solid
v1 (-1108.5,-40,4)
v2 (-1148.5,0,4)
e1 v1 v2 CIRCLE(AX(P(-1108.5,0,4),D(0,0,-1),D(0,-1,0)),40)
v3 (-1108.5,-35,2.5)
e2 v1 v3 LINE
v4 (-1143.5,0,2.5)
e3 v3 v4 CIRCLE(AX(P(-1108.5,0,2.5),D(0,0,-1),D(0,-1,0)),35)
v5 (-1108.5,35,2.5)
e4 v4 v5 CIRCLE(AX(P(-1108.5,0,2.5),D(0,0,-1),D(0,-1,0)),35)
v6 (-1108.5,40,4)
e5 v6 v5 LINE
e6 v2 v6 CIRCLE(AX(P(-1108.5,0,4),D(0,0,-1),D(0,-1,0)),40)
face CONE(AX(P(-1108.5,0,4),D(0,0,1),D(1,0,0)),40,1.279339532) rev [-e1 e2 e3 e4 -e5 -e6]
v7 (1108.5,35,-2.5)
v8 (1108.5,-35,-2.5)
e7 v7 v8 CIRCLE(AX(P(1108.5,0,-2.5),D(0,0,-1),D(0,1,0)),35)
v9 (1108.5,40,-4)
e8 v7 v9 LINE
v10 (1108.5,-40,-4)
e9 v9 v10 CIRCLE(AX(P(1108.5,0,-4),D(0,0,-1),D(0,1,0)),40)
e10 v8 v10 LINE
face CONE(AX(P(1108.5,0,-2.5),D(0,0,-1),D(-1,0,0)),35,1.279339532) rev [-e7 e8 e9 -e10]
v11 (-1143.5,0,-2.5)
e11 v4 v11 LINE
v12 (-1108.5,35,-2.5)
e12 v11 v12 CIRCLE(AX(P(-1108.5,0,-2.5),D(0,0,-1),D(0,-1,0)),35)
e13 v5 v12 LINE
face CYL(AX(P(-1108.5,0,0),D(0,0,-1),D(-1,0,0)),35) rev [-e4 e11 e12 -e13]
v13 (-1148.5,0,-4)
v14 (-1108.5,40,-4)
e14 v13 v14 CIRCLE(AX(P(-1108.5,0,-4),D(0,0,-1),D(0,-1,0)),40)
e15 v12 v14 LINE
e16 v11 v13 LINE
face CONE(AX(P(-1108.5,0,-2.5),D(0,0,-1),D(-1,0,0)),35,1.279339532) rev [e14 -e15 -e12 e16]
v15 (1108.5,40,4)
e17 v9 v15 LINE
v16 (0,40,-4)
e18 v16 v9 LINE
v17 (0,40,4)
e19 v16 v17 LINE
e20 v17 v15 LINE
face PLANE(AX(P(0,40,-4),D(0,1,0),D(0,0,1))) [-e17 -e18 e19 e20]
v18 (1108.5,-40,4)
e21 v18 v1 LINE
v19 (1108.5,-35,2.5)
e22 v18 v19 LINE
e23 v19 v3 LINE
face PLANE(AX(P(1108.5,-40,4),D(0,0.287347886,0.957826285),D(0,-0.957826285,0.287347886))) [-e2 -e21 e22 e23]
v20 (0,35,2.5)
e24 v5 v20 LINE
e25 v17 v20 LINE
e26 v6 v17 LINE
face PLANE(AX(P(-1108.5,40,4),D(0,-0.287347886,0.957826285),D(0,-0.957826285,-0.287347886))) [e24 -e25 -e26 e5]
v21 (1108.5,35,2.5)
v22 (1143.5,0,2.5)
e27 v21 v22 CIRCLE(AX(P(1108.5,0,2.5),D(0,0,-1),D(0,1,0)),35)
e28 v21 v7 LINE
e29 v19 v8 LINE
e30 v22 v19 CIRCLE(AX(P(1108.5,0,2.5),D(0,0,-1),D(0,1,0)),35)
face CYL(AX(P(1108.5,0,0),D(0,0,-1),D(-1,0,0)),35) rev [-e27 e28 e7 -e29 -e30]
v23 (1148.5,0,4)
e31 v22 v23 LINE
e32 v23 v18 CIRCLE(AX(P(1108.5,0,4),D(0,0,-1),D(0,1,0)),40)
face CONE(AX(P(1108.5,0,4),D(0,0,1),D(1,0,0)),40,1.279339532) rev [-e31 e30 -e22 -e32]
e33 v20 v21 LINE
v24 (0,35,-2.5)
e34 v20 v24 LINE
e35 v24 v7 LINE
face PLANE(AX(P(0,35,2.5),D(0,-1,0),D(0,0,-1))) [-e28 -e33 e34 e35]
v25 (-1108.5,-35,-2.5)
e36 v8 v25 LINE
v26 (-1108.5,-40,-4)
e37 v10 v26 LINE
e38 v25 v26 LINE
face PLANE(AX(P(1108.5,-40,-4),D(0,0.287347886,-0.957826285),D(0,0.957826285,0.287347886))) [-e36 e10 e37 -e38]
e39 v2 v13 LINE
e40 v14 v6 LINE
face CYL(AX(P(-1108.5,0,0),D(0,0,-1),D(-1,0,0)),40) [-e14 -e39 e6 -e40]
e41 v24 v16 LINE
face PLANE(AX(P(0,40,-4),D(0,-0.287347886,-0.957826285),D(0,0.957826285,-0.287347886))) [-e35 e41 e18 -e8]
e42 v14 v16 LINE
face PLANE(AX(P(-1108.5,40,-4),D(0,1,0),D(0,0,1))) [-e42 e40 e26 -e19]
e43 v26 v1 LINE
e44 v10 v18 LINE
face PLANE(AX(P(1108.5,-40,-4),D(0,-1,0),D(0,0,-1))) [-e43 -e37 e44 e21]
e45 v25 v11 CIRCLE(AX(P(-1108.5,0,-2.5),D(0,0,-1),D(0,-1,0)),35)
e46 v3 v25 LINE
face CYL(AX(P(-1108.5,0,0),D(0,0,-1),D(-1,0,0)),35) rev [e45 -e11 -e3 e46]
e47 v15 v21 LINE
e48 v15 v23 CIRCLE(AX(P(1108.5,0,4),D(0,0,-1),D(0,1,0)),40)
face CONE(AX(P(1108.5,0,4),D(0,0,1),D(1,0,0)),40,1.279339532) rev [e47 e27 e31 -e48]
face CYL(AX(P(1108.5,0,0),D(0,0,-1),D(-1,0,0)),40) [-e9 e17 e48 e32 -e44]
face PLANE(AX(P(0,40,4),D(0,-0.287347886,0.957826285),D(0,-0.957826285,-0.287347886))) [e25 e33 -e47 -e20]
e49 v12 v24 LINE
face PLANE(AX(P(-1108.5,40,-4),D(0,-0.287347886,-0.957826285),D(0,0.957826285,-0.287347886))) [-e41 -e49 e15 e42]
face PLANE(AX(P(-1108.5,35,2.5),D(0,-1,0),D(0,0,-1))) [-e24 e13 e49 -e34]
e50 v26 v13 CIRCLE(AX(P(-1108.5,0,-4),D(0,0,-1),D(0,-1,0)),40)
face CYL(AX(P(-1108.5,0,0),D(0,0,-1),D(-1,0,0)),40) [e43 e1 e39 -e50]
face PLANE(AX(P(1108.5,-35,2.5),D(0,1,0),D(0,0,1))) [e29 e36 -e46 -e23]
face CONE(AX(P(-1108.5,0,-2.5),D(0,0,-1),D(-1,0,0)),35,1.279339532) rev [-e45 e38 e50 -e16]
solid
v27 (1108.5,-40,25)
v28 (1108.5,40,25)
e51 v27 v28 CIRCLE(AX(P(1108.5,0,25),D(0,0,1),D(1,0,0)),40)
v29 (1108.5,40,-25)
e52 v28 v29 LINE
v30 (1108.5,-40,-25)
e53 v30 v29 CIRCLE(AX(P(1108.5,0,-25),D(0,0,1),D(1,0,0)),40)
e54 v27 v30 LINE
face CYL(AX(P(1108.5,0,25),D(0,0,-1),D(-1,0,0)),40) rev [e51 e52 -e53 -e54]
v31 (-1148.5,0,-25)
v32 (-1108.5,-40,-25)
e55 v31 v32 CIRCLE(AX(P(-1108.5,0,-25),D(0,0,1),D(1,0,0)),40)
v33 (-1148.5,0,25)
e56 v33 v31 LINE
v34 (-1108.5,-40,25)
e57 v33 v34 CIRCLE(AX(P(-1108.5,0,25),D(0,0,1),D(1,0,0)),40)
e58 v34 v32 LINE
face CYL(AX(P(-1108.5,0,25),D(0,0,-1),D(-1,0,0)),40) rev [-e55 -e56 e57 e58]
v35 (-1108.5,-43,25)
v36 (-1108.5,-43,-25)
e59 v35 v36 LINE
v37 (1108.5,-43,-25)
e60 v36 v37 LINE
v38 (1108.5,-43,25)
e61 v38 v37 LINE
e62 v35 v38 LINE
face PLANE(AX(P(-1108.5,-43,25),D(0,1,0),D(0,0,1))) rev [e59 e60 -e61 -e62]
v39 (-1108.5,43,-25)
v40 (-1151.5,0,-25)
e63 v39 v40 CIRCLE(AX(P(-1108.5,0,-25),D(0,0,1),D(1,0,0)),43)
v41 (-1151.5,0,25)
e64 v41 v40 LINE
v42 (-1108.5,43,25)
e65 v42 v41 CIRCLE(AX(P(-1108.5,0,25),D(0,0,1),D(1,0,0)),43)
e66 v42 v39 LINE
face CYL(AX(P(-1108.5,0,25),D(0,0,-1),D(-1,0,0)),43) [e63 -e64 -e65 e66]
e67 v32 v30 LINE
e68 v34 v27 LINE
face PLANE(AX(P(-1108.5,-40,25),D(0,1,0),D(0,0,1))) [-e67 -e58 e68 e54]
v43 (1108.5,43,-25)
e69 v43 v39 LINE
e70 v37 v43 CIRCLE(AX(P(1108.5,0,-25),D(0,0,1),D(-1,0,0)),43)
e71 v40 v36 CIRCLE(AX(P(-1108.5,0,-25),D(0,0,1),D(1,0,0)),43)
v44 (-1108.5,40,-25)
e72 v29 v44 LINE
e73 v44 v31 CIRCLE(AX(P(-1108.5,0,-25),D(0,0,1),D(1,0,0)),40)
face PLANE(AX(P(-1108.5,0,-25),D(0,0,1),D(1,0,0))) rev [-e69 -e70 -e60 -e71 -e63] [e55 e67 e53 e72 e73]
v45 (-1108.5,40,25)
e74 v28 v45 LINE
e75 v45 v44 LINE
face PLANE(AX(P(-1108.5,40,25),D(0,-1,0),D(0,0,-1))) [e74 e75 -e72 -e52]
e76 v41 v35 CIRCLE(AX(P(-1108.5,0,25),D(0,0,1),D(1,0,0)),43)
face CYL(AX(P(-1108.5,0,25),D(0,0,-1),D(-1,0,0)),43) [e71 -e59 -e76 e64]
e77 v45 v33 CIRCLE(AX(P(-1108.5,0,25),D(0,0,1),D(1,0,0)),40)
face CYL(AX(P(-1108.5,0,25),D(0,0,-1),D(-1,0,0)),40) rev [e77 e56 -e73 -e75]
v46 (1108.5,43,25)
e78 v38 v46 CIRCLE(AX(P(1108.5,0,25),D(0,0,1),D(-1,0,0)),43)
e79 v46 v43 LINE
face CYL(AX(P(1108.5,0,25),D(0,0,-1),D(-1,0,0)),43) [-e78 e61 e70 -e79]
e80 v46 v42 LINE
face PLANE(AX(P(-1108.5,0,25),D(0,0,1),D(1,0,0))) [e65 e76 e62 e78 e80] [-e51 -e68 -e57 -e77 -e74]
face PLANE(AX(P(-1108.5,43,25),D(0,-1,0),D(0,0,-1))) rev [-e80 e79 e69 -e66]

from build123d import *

# Parameters (mm, degrees)
EXTRUDE_1_DEPTH = 25


with BuildPart() as part:
    # 草图1 → 拉伸-薄壁1 (new, symmetric)
    with BuildSketch(Plane.XY):
        with BuildLine():
            Line((1108.5, -43), (-1108.5, -43))
            ThreePointArc((-1108.5, -43), (-1151.5, 0), (-1108.5, 43))
            Line((-1108.5, 43), (1108.5, 43))
            ThreePointArc((1108.5, 43), (1151.5, 0), (1108.5, -43))
        make_face()
        with BuildLine():
            Line((1108.5, -40), (-1108.5, -40))
            ThreePointArc((-1108.5, -40), (-1148.5, 0), (-1108.5, 40))
            Line((-1108.5, 40), (1108.5, 40))
            ThreePointArc((1108.5, 40), (1148.5, 0), (1108.5, -40))
        make_face(mode=Mode.SUBTRACT)
    extrude(amount=EXTRUDE_1_DEPTH, both=True)


with BuildPart() as body_2:
    # 扫描1: sweep along a path in 草图2
    with BuildLine(Plane.XY) as sweep_1_path:
        Line((-1108.5, -40), (1108.5, -40))
        ThreePointArc((1108.5, -40), (1148.5, 0), (1108.5, 40))
        Line((1108.5, 40), (-1108.5, 40))
        ThreePointArc((-1108.5, 40), (-1148.5, 0), (-1108.5, -40))
    # 草图3 → 扫描1 (sweep)
    with BuildSketch(Plane(origin=(0, 0, 0), x_dir=(0, 0, -1), z_dir=(1, 0, 0))):
        Polygon((4, 40), (-4, 40), (-2.5, 35), (2.5, 35), align=None)
    sweep(path=sweep_1_path.line)


solid = Compound([part.part, body_2.part])
